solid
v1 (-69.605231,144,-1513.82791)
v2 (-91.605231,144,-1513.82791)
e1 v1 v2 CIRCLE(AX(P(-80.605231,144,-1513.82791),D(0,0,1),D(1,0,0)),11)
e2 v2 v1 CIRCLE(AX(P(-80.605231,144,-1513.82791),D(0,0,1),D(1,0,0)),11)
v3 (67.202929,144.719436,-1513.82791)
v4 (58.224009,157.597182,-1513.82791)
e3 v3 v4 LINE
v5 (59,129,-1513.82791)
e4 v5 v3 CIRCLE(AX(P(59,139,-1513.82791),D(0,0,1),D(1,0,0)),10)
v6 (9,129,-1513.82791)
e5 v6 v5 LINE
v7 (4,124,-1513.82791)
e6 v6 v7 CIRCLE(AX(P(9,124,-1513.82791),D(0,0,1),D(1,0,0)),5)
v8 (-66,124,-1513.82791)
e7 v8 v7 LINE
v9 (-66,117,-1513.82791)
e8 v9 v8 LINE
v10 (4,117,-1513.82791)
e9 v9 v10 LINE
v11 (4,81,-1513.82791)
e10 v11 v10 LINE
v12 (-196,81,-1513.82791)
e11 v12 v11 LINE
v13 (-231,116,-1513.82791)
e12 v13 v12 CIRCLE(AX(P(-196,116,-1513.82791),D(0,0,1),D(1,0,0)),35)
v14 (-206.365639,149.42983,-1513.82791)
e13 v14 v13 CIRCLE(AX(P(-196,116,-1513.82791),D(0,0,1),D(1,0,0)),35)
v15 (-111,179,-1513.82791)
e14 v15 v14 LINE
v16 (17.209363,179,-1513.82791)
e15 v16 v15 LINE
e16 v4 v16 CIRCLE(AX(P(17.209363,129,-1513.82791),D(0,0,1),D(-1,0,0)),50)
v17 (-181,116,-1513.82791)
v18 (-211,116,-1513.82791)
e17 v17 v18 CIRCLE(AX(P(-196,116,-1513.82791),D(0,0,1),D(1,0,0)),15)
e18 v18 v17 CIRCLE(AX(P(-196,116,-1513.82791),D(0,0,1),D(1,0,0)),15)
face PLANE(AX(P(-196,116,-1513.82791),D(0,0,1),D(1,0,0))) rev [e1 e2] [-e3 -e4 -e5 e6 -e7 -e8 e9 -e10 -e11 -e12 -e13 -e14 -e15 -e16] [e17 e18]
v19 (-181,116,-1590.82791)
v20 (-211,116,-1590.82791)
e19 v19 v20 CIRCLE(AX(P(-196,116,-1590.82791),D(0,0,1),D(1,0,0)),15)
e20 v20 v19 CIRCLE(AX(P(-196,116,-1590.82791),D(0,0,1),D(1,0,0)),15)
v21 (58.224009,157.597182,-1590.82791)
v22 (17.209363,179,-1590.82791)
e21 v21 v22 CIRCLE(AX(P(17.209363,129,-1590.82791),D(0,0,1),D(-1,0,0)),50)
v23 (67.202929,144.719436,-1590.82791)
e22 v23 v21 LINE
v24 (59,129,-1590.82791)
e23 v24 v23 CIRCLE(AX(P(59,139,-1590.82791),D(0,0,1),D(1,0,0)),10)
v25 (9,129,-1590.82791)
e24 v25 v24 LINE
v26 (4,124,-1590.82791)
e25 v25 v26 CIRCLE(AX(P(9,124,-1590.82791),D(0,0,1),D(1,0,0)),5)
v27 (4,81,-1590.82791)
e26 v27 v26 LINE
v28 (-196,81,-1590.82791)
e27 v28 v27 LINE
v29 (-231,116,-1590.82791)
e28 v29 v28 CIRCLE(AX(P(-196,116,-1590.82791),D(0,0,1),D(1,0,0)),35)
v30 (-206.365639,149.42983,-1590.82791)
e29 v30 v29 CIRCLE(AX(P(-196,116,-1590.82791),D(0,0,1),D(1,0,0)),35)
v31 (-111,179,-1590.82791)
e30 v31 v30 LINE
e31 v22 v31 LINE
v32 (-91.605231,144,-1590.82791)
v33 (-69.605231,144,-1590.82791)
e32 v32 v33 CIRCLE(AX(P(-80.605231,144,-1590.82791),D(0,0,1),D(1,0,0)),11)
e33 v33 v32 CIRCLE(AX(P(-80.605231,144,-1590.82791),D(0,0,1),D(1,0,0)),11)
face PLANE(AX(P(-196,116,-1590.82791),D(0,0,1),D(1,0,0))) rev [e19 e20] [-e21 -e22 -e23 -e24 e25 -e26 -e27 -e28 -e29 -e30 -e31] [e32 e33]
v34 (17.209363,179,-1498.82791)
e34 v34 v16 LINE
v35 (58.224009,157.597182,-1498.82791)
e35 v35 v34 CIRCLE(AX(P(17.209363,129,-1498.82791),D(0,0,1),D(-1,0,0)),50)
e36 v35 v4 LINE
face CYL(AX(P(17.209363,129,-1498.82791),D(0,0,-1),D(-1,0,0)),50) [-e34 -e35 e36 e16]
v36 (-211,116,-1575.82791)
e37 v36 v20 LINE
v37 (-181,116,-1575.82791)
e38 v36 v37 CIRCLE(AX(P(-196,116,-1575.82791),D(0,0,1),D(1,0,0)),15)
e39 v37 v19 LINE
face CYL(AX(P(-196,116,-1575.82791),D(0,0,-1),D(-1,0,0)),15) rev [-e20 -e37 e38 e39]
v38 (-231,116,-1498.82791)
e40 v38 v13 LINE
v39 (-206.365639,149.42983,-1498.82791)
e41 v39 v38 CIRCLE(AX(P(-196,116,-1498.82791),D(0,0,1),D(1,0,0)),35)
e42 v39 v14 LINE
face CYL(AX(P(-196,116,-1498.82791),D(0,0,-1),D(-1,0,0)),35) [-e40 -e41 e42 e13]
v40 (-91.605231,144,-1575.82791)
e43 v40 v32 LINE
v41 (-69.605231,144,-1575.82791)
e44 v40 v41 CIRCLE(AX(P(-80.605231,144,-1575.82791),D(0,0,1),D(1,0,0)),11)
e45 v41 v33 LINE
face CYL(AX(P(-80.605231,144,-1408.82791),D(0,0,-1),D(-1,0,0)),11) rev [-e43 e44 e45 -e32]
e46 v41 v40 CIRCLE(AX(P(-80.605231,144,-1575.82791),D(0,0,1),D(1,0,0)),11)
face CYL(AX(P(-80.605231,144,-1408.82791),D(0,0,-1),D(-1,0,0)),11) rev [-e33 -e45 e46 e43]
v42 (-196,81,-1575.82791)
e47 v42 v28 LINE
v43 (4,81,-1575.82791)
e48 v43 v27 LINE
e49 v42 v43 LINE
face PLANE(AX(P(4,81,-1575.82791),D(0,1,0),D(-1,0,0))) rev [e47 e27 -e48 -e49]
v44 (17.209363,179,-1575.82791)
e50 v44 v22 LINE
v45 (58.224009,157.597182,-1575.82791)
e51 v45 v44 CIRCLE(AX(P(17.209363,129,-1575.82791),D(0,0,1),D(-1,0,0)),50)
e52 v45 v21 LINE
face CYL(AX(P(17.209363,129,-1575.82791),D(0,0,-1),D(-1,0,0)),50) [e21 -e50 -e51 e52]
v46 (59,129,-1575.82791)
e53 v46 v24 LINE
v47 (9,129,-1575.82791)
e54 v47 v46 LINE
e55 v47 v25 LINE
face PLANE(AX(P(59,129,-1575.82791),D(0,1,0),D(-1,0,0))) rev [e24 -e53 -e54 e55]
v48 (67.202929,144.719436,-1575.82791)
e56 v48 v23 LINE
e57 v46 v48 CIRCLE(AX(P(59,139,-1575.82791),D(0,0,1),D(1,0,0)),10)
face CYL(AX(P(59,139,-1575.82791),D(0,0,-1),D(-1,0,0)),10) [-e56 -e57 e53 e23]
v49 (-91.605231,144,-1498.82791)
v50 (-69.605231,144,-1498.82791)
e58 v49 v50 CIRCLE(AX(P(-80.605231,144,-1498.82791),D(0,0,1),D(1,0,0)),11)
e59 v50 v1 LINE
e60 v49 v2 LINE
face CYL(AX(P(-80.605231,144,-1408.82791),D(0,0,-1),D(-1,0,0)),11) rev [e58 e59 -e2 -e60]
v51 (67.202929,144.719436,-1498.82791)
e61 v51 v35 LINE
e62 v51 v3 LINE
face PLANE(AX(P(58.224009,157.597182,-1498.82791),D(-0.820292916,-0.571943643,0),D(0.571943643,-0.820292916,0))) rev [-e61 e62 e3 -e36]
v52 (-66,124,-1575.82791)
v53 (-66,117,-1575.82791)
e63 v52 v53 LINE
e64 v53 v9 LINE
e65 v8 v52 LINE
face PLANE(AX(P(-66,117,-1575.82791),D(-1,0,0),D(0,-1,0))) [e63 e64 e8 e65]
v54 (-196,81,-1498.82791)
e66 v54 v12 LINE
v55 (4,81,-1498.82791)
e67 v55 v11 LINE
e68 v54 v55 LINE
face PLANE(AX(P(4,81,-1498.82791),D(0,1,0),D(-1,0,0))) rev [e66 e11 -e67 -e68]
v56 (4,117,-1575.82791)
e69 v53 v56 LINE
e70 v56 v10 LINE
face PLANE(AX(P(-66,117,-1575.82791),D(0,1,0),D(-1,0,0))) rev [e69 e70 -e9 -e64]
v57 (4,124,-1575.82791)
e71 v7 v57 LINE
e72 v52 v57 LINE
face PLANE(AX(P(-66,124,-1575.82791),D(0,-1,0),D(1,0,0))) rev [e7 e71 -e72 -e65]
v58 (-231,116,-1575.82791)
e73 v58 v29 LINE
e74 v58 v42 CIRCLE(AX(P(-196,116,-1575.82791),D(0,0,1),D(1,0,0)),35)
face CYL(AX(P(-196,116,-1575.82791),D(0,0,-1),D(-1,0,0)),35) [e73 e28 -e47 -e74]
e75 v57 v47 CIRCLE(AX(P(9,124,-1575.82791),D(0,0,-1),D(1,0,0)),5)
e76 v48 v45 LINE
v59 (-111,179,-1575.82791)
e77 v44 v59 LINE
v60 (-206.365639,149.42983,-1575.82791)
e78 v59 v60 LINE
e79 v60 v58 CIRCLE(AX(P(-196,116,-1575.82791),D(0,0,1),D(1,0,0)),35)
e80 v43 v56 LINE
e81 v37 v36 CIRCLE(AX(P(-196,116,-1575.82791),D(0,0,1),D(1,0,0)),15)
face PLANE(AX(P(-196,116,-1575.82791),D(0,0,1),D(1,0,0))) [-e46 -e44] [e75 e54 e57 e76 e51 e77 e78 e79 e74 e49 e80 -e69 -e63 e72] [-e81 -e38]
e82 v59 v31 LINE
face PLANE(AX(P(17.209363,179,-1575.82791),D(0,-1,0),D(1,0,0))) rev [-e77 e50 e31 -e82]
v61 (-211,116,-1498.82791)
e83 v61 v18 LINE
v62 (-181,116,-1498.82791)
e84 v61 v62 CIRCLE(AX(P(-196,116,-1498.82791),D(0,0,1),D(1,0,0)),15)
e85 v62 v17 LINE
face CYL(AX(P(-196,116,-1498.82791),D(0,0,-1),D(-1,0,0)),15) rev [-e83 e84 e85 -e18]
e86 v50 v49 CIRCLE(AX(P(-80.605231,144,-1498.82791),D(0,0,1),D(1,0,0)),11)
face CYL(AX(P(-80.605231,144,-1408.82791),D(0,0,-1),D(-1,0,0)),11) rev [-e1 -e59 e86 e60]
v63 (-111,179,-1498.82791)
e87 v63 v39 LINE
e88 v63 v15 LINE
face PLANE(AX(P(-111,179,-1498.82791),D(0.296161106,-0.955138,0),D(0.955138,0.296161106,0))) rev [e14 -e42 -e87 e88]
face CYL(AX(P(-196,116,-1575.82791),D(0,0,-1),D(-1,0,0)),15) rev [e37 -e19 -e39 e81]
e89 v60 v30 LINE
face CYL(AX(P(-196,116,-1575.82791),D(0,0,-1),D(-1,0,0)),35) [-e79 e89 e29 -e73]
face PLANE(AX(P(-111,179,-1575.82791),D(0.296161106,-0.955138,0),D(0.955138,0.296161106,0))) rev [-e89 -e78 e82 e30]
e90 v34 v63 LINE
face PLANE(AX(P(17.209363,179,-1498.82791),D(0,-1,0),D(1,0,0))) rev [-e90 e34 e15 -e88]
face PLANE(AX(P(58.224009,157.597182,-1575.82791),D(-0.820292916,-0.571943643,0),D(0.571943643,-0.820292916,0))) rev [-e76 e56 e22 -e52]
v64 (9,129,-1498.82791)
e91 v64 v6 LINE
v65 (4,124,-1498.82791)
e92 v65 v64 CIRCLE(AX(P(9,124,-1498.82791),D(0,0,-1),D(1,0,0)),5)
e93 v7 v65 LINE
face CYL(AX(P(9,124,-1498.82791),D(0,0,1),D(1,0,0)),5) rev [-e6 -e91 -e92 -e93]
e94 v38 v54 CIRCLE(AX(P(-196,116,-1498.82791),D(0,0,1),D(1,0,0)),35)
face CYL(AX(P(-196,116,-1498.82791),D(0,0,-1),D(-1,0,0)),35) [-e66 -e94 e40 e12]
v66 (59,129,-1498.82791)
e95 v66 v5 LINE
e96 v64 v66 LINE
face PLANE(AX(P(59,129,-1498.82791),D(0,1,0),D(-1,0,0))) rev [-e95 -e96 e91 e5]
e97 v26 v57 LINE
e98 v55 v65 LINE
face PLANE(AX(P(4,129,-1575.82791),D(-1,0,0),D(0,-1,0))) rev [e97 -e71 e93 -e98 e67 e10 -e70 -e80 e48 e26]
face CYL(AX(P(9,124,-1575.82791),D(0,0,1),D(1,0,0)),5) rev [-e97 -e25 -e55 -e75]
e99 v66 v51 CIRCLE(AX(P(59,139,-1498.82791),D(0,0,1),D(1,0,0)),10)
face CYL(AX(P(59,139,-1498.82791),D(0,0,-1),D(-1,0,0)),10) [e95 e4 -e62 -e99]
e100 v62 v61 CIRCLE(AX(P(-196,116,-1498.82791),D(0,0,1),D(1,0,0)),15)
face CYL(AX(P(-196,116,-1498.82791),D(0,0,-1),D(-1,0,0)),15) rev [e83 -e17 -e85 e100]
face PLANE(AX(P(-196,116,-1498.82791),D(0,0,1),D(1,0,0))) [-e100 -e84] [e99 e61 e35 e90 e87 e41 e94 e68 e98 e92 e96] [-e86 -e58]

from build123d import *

# Parameters (mm, degrees)
EXTRUDE_START          = 700
SKETCH_1_R             = 15
EXTRUDE_1_DEPTH        = 15
PATTERN_LINEAR_1_COUNT = 2
PATTERN_LINEAR_1_PITCH = 77
SKETCH_2_W             = 62
SKETCH_2_H             = 7
EXTRUDE_2_DEPTH        = 70
SKETCH_3_R             = 11
CUT_EXTRUDE_2_DEPTH    = 105
FILLET_1_R             = 5


with BuildPart() as part:
    # 草图1 → 凸台-拉伸1 (new body)
    with BuildSketch(Plane.XY.offset(-2290.827909759).offset(EXTRUDE_START)):
        with BuildLine():
            Line((4, 81), (-196, 81))
            ThreePointArc((-196, 81), (-230.605231181, 110.758056189), (-206.365638709, 149.429830005))
            Line((-206.365638709, 149.429830005), (-111, 179))
            Line((-111, 179), (17.209362926, 179))
            ThreePointArc((17.209362926, 179), (40.340952707, 173.32752592), (58.22400875, 157.597182169))
            Line((58.22400875, 157.597182169), (67.202929165, 144.719436434))
            ThreePointArc((67.202929165, 144.719436434), (67.865505184, 134.373682044), (59, 129))
            Line((59, 129), (4, 129))
            Line((4, 129), (4, 81))
        make_face()
        with Locations((-196, 116)):
            Circle(SKETCH_1_R, mode=Mode.SUBTRACT)
    extrude(amount=EXTRUDE_1_DEPTH)


with BuildPart() as pattern_linear_1_1:
    # 阵列(线性)1: pattern copy
    add(part.part.moved(Location(Vector(0, 0, 1) * (1 * PATTERN_LINEAR_1_PITCH))))


with BuildPart() as part_1:
    add(part.part)

    add(pattern_linear_1_1.part)  # 凸台-拉伸2 merges 阵列(线性)1_1
    # 草图2 → 凸台-拉伸2 (add)
    with BuildSketch(Plane.ZY.offset(-4)):
        with Locations((-1544.827909759, 120.5)):
            Rectangle(SKETCH_2_W, SKETCH_2_H)
    extrude(amount=EXTRUDE_2_DEPTH)

    # 草图3 → 切除-拉伸2 (cut, symmetric)
    with BuildSketch(Plane(origin=(0, 0, -1513.827909759), x_dir=(-1, 0, 0), z_dir=(0, 0, -1))):
        with Locations(Location((80.605231181, 144, 0), (0, 0, 180))):
            Circle(SKETCH_3_R)
    extrude(amount=CUT_EXTRUDE_2_DEPTH, both=True, mode=Mode.SUBTRACT)

    # 圆角1
    fillet_1_edges = [part_1.edges().sort_by_distance(p)[0] for p in [
        (4, 129, -1583.327909759),
        (4, 129, -1506.327909759),
    ]]
    fillet(fillet_1_edges, radius=FILLET_1_R)


solid = part_1.part
